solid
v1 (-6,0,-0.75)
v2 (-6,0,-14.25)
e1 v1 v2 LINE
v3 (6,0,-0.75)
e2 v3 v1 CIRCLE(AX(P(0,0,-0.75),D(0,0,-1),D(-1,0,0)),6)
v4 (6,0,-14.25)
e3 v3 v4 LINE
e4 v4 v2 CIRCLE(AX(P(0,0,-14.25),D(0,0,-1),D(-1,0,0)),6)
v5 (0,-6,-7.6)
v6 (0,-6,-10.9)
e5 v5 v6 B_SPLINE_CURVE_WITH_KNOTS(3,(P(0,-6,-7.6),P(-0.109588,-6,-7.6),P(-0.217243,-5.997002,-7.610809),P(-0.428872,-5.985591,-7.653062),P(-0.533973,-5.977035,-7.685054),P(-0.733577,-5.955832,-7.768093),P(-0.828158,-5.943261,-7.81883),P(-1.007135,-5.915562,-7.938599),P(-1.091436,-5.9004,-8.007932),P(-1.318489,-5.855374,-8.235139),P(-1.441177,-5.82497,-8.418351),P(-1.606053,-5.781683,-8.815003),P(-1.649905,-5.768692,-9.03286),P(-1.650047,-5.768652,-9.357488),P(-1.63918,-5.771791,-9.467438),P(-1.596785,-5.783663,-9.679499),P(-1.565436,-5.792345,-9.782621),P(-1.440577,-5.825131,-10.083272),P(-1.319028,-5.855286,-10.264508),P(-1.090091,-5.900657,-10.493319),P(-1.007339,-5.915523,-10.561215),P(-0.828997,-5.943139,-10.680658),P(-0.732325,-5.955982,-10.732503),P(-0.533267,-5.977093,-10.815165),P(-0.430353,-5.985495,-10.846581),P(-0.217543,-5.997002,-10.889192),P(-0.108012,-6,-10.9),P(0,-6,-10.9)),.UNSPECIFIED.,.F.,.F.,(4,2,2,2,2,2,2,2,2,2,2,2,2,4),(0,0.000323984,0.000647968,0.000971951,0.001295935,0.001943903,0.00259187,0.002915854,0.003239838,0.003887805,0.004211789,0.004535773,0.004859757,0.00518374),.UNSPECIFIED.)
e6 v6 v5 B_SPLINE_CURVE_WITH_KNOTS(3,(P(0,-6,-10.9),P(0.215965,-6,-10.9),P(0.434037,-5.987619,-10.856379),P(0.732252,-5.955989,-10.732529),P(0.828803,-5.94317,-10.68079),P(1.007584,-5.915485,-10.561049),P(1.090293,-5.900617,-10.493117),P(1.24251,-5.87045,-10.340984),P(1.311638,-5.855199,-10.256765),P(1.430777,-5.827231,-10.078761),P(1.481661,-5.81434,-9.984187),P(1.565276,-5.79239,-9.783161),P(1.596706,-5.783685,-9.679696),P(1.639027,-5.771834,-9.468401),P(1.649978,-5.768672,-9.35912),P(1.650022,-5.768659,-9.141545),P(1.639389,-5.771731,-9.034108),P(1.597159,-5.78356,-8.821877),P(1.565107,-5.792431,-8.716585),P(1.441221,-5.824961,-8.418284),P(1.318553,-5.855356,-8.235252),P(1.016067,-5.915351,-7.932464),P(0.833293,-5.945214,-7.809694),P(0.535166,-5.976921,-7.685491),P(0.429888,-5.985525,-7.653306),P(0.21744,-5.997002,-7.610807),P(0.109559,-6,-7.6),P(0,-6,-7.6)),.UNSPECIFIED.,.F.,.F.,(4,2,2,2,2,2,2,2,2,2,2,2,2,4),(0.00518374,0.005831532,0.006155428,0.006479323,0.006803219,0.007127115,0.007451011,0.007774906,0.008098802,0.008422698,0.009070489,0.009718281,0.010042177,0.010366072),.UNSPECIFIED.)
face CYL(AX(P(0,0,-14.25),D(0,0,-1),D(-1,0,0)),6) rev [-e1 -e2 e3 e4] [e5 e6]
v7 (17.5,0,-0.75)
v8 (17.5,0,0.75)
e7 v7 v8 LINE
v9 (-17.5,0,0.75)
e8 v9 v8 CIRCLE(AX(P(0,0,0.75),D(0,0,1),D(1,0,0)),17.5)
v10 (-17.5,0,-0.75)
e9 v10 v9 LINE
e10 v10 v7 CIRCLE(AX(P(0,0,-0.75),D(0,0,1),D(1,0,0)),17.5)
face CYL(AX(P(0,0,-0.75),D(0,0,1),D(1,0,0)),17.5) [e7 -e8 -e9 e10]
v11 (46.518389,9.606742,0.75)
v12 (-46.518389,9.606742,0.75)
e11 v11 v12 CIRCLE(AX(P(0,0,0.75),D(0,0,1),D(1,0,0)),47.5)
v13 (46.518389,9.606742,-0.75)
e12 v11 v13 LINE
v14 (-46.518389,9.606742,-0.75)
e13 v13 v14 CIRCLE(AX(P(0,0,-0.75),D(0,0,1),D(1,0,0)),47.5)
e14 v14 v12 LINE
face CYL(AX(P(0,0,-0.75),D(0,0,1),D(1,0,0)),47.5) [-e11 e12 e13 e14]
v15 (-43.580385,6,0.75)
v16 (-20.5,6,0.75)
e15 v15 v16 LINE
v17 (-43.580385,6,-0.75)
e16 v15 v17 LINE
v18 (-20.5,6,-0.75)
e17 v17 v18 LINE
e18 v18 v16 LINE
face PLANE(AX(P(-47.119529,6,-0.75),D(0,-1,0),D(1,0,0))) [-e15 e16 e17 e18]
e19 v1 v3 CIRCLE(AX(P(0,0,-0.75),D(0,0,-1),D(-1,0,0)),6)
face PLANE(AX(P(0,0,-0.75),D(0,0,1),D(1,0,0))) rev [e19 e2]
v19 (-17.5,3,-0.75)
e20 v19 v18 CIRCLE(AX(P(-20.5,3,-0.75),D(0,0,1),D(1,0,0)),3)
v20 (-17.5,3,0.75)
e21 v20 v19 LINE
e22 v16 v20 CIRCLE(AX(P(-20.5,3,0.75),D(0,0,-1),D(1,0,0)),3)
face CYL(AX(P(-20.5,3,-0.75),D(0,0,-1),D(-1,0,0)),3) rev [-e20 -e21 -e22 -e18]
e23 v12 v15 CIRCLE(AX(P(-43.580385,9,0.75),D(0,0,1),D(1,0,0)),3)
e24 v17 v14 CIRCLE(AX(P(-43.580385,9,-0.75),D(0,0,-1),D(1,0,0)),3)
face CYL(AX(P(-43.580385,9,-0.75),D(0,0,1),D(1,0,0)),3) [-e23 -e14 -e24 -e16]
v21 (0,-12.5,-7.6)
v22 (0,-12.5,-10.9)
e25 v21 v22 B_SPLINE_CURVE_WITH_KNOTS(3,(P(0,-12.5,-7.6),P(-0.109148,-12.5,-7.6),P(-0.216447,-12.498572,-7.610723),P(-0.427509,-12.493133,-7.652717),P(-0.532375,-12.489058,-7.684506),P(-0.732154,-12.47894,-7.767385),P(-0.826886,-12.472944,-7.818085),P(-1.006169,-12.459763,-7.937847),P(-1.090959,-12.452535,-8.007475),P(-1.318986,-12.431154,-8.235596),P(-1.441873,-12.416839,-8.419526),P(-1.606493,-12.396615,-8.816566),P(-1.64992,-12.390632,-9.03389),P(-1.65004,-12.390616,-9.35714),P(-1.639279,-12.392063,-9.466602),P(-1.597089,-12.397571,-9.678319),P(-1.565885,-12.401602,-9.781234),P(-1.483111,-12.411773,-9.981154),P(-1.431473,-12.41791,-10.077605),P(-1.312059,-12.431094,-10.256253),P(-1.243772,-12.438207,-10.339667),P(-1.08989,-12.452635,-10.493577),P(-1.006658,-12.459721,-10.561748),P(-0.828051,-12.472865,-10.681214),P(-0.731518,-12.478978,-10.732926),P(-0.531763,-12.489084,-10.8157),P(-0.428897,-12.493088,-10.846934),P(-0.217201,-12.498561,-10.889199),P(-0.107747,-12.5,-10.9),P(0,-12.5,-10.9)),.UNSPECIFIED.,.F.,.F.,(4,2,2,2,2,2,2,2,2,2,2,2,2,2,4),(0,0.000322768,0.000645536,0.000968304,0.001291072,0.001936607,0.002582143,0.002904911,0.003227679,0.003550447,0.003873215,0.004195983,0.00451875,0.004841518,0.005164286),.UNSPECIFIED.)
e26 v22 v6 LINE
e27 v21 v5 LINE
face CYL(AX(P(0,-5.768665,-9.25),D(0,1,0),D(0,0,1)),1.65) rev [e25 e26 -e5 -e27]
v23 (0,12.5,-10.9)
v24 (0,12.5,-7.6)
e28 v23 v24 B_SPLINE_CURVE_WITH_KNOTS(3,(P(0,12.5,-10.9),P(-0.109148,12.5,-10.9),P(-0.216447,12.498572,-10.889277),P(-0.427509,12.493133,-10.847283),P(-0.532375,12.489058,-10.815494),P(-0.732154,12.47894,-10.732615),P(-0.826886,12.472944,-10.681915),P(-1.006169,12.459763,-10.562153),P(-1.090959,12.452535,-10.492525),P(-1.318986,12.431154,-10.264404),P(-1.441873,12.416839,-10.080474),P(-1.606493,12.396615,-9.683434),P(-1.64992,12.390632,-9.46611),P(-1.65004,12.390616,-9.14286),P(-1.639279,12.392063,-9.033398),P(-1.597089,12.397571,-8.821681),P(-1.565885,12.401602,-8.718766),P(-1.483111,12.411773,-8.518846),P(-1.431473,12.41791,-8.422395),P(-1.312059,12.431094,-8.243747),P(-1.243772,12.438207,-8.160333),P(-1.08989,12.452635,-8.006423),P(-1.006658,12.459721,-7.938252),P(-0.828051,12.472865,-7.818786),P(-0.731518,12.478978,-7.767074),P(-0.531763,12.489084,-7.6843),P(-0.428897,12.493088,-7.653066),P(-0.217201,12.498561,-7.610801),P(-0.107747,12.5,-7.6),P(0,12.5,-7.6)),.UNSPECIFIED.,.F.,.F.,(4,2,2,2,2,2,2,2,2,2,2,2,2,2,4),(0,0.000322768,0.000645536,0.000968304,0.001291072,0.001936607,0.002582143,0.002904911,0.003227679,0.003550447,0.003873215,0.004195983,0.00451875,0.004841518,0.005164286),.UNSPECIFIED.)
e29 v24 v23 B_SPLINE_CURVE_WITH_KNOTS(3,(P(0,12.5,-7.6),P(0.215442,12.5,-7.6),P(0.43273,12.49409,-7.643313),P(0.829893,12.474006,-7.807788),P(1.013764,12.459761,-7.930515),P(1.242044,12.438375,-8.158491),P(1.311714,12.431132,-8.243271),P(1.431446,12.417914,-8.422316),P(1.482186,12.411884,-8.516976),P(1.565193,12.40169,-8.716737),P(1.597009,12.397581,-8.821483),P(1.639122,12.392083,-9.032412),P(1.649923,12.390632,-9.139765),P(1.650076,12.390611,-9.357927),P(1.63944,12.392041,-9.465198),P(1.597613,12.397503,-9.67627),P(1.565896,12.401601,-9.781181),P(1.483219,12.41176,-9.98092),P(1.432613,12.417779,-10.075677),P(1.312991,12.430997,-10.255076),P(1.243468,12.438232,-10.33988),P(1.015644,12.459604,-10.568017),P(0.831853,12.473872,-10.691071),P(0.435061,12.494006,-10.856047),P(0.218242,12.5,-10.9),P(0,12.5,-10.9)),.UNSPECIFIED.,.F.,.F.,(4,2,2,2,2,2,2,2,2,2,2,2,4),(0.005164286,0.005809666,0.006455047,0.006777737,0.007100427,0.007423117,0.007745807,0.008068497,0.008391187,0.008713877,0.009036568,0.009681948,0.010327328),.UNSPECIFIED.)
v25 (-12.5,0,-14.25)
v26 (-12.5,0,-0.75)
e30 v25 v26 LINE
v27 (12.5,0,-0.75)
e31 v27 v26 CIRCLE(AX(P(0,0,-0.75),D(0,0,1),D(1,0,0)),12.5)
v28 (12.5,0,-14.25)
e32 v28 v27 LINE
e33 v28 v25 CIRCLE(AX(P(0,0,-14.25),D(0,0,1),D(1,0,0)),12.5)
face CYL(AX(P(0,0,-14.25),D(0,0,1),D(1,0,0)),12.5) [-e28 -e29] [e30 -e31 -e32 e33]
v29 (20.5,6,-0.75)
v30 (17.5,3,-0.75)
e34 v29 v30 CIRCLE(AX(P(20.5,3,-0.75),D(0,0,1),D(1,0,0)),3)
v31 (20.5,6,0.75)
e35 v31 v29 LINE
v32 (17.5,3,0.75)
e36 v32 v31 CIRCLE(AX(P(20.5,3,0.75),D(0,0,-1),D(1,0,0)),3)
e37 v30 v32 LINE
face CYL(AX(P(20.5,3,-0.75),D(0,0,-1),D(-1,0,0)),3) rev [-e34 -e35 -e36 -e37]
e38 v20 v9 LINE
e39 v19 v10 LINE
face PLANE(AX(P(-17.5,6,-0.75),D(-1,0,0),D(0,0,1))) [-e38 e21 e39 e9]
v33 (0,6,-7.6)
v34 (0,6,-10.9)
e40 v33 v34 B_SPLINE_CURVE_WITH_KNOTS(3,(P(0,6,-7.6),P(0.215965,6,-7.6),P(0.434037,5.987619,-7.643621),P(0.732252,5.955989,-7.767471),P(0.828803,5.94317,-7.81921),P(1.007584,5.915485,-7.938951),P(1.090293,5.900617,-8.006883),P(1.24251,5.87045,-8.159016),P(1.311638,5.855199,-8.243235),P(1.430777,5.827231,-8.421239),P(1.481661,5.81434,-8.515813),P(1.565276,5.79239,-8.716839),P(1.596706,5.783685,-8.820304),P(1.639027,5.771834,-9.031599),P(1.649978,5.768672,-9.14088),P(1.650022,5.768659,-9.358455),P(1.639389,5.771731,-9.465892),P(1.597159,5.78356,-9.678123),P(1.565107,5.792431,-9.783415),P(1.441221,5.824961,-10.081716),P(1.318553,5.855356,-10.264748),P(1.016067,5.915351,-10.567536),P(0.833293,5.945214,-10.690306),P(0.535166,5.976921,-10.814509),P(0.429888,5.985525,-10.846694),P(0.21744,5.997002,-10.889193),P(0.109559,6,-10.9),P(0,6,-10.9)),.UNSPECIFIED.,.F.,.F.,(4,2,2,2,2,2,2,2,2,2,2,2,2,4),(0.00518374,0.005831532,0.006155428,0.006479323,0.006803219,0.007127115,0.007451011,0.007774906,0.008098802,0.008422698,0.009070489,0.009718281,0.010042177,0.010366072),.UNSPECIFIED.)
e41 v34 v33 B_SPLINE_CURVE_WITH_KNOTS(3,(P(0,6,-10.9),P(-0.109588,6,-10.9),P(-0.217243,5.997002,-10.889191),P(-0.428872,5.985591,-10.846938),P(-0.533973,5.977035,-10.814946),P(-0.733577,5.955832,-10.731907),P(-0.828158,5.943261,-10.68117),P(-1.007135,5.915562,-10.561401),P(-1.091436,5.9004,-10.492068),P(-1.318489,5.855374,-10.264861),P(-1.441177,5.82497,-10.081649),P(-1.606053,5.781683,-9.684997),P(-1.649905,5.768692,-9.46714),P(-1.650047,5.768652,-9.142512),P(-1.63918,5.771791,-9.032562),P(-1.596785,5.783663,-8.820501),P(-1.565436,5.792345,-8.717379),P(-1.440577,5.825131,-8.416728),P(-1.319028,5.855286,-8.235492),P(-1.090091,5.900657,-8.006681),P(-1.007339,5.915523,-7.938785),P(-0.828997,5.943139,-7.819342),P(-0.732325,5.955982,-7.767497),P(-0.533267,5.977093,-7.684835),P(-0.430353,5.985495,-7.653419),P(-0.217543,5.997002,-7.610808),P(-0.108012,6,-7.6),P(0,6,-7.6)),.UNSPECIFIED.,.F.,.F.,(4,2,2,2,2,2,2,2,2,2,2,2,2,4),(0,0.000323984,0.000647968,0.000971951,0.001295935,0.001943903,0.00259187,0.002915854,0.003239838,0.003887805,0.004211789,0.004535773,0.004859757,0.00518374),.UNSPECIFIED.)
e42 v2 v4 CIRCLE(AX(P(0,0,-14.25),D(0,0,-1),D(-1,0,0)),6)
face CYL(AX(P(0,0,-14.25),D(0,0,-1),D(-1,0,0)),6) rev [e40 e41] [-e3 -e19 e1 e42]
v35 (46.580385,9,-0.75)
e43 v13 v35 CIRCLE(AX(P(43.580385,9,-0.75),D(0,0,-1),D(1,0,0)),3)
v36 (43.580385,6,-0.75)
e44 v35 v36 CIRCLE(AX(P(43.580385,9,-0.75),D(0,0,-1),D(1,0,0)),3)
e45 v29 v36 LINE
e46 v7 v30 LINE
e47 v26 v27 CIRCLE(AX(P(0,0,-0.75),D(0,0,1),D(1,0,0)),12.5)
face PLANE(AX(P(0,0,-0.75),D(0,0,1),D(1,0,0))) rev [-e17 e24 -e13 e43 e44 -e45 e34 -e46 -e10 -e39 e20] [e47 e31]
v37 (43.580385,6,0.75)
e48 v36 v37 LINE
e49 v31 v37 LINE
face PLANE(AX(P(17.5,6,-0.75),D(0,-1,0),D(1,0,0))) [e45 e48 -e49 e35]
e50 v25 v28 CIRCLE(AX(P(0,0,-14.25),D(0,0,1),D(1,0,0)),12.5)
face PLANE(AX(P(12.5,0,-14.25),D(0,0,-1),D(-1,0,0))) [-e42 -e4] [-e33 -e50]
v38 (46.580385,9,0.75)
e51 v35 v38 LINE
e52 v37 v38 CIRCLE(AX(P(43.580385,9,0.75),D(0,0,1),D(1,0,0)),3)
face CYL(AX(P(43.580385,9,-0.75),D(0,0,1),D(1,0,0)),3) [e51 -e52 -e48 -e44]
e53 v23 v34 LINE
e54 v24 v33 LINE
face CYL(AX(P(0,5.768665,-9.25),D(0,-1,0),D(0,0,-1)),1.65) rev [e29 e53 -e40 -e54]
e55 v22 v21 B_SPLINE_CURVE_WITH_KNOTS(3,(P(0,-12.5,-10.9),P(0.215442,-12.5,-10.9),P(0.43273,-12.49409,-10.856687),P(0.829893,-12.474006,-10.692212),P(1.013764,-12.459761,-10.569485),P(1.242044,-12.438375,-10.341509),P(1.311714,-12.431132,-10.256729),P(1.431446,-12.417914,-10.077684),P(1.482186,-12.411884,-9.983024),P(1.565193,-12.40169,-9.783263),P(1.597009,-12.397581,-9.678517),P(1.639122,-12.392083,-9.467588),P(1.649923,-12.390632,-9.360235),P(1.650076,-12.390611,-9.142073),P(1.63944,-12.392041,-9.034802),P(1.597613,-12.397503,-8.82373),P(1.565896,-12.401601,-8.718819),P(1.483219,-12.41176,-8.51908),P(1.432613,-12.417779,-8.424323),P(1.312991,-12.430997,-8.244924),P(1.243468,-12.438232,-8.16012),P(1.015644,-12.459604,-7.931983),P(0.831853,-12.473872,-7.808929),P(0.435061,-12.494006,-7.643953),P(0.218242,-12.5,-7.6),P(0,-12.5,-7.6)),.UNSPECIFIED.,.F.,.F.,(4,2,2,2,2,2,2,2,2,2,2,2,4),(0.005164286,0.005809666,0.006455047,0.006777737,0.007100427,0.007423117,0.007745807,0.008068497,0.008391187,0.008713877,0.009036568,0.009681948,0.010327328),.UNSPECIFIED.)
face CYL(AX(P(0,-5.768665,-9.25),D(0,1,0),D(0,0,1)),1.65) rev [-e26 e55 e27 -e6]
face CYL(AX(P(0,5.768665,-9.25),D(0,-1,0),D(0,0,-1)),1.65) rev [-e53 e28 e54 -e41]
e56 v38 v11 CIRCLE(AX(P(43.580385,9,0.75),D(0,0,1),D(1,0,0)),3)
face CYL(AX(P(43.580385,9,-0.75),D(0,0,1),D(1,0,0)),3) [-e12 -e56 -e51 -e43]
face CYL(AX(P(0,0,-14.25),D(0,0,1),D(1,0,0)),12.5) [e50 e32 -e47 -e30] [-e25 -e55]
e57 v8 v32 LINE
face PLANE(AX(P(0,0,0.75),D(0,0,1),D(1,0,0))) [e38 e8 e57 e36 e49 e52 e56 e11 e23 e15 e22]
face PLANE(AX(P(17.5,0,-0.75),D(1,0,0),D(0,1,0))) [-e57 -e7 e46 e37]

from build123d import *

# Parameters (mm, degrees)
EXTRUDE_1_DEPTH             = 1.5
SKETCH_2_W                  = 12.5
SKETCH_2_H                  = 13.5
HOLE_WIZARD_12_0_12_1_D     = 12
HOLE_WIZARD_12_0_12_1_DEPTH = 13.5
SKETCH_5_W                  = 1.65
SKETCH_5_H                  = 11.731334643
HOLE_WIZARD_3_3_3_3_2_D     = 3.3
HOLE_WIZARD_3_3_3_3_2_DEPTH = 41.731334643
FILLET_1_R                  = 3


with BuildPart() as part:
    # 草图1 → 凸台-拉伸1 (new body)
    with BuildSketch(Plane.XY.offset(0.75)):
        with BuildLine():
            Line((17.5, 6), (47.11952886, 6))
            ThreePointArc((47.11952886, 6), (0, 47.5), (-47.11952886, 6))
            Line((-47.11952886, 6), (-17.5, 6))
            Line((-17.5, 6), (-17.5, 0))
            ThreePointArc((-17.5, 0), (0, -17.5), (17.5, 0))
            Line((17.5, 0), (17.5, 6))
        make_face()
    extrude(amount=-EXTRUDE_1_DEPTH)

    # 草图2 → 旋转1 (revolve)
    with BuildSketch(Plane(origin=(0, 0, 0), x_dir=(1, 0, 0), z_dir=(0, 1, 0))):
        with Locations((6.25, 7.5)):
            Rectangle(SKETCH_2_W, SKETCH_2_H)
    revolve(axis=Axis((0, 0, -14.25), (0, 0, 1)))

    # Ø12.0 (12) 直径孔1
    with Locations(Plane(origin=(0, 0, -14.25), x_dir=(-1, 0, 0), z_dir=(0, 0, -1))):
        with Locations((0, 0)):
            Hole(HOLE_WIZARD_12_0_12_1_D / 2, depth=HOLE_WIZARD_12_0_12_1_DEPTH)

    # 草图5 → Ø3.3 (3.3) 直径孔1 (revolve, cut)
    with BuildSketch(Plane(origin=(0, -5.768665357, -9.25), x_dir=(0, 0, 1), z_dir=(1, 0, 0))):
        with Locations((0.825, 5.865667322)):
            Rectangle(SKETCH_5_W, SKETCH_5_H)
    revolve(axis=Axis((0, 0.581334643, -9.25), (0, -1, 0)), mode=Mode.SUBTRACT)

    # Ø3.3 (3.3) 直径孔2
    with Locations(Plane(origin=(0, 5.768665357, 0), x_dir=(-1, 0, 0), z_dir=(0, -1, 0))):
        with Locations((0, 9.25)):
            Hole(HOLE_WIZARD_3_3_3_3_2_D / 2, depth=HOLE_WIZARD_3_3_3_3_2_DEPTH)

    # 圆角1
    fillet_1_edges = [part.edges().sort_by_distance(p)[0] for p in [
        (-17.5, 6, 0),
        (-47.11952886, 6, 0),
        (47.11952886, 6, 0),
        (17.5, 6, 0),
    ]]
    fillet(fillet_1_edges, radius=FILLET_1_R)


solid = part.part
